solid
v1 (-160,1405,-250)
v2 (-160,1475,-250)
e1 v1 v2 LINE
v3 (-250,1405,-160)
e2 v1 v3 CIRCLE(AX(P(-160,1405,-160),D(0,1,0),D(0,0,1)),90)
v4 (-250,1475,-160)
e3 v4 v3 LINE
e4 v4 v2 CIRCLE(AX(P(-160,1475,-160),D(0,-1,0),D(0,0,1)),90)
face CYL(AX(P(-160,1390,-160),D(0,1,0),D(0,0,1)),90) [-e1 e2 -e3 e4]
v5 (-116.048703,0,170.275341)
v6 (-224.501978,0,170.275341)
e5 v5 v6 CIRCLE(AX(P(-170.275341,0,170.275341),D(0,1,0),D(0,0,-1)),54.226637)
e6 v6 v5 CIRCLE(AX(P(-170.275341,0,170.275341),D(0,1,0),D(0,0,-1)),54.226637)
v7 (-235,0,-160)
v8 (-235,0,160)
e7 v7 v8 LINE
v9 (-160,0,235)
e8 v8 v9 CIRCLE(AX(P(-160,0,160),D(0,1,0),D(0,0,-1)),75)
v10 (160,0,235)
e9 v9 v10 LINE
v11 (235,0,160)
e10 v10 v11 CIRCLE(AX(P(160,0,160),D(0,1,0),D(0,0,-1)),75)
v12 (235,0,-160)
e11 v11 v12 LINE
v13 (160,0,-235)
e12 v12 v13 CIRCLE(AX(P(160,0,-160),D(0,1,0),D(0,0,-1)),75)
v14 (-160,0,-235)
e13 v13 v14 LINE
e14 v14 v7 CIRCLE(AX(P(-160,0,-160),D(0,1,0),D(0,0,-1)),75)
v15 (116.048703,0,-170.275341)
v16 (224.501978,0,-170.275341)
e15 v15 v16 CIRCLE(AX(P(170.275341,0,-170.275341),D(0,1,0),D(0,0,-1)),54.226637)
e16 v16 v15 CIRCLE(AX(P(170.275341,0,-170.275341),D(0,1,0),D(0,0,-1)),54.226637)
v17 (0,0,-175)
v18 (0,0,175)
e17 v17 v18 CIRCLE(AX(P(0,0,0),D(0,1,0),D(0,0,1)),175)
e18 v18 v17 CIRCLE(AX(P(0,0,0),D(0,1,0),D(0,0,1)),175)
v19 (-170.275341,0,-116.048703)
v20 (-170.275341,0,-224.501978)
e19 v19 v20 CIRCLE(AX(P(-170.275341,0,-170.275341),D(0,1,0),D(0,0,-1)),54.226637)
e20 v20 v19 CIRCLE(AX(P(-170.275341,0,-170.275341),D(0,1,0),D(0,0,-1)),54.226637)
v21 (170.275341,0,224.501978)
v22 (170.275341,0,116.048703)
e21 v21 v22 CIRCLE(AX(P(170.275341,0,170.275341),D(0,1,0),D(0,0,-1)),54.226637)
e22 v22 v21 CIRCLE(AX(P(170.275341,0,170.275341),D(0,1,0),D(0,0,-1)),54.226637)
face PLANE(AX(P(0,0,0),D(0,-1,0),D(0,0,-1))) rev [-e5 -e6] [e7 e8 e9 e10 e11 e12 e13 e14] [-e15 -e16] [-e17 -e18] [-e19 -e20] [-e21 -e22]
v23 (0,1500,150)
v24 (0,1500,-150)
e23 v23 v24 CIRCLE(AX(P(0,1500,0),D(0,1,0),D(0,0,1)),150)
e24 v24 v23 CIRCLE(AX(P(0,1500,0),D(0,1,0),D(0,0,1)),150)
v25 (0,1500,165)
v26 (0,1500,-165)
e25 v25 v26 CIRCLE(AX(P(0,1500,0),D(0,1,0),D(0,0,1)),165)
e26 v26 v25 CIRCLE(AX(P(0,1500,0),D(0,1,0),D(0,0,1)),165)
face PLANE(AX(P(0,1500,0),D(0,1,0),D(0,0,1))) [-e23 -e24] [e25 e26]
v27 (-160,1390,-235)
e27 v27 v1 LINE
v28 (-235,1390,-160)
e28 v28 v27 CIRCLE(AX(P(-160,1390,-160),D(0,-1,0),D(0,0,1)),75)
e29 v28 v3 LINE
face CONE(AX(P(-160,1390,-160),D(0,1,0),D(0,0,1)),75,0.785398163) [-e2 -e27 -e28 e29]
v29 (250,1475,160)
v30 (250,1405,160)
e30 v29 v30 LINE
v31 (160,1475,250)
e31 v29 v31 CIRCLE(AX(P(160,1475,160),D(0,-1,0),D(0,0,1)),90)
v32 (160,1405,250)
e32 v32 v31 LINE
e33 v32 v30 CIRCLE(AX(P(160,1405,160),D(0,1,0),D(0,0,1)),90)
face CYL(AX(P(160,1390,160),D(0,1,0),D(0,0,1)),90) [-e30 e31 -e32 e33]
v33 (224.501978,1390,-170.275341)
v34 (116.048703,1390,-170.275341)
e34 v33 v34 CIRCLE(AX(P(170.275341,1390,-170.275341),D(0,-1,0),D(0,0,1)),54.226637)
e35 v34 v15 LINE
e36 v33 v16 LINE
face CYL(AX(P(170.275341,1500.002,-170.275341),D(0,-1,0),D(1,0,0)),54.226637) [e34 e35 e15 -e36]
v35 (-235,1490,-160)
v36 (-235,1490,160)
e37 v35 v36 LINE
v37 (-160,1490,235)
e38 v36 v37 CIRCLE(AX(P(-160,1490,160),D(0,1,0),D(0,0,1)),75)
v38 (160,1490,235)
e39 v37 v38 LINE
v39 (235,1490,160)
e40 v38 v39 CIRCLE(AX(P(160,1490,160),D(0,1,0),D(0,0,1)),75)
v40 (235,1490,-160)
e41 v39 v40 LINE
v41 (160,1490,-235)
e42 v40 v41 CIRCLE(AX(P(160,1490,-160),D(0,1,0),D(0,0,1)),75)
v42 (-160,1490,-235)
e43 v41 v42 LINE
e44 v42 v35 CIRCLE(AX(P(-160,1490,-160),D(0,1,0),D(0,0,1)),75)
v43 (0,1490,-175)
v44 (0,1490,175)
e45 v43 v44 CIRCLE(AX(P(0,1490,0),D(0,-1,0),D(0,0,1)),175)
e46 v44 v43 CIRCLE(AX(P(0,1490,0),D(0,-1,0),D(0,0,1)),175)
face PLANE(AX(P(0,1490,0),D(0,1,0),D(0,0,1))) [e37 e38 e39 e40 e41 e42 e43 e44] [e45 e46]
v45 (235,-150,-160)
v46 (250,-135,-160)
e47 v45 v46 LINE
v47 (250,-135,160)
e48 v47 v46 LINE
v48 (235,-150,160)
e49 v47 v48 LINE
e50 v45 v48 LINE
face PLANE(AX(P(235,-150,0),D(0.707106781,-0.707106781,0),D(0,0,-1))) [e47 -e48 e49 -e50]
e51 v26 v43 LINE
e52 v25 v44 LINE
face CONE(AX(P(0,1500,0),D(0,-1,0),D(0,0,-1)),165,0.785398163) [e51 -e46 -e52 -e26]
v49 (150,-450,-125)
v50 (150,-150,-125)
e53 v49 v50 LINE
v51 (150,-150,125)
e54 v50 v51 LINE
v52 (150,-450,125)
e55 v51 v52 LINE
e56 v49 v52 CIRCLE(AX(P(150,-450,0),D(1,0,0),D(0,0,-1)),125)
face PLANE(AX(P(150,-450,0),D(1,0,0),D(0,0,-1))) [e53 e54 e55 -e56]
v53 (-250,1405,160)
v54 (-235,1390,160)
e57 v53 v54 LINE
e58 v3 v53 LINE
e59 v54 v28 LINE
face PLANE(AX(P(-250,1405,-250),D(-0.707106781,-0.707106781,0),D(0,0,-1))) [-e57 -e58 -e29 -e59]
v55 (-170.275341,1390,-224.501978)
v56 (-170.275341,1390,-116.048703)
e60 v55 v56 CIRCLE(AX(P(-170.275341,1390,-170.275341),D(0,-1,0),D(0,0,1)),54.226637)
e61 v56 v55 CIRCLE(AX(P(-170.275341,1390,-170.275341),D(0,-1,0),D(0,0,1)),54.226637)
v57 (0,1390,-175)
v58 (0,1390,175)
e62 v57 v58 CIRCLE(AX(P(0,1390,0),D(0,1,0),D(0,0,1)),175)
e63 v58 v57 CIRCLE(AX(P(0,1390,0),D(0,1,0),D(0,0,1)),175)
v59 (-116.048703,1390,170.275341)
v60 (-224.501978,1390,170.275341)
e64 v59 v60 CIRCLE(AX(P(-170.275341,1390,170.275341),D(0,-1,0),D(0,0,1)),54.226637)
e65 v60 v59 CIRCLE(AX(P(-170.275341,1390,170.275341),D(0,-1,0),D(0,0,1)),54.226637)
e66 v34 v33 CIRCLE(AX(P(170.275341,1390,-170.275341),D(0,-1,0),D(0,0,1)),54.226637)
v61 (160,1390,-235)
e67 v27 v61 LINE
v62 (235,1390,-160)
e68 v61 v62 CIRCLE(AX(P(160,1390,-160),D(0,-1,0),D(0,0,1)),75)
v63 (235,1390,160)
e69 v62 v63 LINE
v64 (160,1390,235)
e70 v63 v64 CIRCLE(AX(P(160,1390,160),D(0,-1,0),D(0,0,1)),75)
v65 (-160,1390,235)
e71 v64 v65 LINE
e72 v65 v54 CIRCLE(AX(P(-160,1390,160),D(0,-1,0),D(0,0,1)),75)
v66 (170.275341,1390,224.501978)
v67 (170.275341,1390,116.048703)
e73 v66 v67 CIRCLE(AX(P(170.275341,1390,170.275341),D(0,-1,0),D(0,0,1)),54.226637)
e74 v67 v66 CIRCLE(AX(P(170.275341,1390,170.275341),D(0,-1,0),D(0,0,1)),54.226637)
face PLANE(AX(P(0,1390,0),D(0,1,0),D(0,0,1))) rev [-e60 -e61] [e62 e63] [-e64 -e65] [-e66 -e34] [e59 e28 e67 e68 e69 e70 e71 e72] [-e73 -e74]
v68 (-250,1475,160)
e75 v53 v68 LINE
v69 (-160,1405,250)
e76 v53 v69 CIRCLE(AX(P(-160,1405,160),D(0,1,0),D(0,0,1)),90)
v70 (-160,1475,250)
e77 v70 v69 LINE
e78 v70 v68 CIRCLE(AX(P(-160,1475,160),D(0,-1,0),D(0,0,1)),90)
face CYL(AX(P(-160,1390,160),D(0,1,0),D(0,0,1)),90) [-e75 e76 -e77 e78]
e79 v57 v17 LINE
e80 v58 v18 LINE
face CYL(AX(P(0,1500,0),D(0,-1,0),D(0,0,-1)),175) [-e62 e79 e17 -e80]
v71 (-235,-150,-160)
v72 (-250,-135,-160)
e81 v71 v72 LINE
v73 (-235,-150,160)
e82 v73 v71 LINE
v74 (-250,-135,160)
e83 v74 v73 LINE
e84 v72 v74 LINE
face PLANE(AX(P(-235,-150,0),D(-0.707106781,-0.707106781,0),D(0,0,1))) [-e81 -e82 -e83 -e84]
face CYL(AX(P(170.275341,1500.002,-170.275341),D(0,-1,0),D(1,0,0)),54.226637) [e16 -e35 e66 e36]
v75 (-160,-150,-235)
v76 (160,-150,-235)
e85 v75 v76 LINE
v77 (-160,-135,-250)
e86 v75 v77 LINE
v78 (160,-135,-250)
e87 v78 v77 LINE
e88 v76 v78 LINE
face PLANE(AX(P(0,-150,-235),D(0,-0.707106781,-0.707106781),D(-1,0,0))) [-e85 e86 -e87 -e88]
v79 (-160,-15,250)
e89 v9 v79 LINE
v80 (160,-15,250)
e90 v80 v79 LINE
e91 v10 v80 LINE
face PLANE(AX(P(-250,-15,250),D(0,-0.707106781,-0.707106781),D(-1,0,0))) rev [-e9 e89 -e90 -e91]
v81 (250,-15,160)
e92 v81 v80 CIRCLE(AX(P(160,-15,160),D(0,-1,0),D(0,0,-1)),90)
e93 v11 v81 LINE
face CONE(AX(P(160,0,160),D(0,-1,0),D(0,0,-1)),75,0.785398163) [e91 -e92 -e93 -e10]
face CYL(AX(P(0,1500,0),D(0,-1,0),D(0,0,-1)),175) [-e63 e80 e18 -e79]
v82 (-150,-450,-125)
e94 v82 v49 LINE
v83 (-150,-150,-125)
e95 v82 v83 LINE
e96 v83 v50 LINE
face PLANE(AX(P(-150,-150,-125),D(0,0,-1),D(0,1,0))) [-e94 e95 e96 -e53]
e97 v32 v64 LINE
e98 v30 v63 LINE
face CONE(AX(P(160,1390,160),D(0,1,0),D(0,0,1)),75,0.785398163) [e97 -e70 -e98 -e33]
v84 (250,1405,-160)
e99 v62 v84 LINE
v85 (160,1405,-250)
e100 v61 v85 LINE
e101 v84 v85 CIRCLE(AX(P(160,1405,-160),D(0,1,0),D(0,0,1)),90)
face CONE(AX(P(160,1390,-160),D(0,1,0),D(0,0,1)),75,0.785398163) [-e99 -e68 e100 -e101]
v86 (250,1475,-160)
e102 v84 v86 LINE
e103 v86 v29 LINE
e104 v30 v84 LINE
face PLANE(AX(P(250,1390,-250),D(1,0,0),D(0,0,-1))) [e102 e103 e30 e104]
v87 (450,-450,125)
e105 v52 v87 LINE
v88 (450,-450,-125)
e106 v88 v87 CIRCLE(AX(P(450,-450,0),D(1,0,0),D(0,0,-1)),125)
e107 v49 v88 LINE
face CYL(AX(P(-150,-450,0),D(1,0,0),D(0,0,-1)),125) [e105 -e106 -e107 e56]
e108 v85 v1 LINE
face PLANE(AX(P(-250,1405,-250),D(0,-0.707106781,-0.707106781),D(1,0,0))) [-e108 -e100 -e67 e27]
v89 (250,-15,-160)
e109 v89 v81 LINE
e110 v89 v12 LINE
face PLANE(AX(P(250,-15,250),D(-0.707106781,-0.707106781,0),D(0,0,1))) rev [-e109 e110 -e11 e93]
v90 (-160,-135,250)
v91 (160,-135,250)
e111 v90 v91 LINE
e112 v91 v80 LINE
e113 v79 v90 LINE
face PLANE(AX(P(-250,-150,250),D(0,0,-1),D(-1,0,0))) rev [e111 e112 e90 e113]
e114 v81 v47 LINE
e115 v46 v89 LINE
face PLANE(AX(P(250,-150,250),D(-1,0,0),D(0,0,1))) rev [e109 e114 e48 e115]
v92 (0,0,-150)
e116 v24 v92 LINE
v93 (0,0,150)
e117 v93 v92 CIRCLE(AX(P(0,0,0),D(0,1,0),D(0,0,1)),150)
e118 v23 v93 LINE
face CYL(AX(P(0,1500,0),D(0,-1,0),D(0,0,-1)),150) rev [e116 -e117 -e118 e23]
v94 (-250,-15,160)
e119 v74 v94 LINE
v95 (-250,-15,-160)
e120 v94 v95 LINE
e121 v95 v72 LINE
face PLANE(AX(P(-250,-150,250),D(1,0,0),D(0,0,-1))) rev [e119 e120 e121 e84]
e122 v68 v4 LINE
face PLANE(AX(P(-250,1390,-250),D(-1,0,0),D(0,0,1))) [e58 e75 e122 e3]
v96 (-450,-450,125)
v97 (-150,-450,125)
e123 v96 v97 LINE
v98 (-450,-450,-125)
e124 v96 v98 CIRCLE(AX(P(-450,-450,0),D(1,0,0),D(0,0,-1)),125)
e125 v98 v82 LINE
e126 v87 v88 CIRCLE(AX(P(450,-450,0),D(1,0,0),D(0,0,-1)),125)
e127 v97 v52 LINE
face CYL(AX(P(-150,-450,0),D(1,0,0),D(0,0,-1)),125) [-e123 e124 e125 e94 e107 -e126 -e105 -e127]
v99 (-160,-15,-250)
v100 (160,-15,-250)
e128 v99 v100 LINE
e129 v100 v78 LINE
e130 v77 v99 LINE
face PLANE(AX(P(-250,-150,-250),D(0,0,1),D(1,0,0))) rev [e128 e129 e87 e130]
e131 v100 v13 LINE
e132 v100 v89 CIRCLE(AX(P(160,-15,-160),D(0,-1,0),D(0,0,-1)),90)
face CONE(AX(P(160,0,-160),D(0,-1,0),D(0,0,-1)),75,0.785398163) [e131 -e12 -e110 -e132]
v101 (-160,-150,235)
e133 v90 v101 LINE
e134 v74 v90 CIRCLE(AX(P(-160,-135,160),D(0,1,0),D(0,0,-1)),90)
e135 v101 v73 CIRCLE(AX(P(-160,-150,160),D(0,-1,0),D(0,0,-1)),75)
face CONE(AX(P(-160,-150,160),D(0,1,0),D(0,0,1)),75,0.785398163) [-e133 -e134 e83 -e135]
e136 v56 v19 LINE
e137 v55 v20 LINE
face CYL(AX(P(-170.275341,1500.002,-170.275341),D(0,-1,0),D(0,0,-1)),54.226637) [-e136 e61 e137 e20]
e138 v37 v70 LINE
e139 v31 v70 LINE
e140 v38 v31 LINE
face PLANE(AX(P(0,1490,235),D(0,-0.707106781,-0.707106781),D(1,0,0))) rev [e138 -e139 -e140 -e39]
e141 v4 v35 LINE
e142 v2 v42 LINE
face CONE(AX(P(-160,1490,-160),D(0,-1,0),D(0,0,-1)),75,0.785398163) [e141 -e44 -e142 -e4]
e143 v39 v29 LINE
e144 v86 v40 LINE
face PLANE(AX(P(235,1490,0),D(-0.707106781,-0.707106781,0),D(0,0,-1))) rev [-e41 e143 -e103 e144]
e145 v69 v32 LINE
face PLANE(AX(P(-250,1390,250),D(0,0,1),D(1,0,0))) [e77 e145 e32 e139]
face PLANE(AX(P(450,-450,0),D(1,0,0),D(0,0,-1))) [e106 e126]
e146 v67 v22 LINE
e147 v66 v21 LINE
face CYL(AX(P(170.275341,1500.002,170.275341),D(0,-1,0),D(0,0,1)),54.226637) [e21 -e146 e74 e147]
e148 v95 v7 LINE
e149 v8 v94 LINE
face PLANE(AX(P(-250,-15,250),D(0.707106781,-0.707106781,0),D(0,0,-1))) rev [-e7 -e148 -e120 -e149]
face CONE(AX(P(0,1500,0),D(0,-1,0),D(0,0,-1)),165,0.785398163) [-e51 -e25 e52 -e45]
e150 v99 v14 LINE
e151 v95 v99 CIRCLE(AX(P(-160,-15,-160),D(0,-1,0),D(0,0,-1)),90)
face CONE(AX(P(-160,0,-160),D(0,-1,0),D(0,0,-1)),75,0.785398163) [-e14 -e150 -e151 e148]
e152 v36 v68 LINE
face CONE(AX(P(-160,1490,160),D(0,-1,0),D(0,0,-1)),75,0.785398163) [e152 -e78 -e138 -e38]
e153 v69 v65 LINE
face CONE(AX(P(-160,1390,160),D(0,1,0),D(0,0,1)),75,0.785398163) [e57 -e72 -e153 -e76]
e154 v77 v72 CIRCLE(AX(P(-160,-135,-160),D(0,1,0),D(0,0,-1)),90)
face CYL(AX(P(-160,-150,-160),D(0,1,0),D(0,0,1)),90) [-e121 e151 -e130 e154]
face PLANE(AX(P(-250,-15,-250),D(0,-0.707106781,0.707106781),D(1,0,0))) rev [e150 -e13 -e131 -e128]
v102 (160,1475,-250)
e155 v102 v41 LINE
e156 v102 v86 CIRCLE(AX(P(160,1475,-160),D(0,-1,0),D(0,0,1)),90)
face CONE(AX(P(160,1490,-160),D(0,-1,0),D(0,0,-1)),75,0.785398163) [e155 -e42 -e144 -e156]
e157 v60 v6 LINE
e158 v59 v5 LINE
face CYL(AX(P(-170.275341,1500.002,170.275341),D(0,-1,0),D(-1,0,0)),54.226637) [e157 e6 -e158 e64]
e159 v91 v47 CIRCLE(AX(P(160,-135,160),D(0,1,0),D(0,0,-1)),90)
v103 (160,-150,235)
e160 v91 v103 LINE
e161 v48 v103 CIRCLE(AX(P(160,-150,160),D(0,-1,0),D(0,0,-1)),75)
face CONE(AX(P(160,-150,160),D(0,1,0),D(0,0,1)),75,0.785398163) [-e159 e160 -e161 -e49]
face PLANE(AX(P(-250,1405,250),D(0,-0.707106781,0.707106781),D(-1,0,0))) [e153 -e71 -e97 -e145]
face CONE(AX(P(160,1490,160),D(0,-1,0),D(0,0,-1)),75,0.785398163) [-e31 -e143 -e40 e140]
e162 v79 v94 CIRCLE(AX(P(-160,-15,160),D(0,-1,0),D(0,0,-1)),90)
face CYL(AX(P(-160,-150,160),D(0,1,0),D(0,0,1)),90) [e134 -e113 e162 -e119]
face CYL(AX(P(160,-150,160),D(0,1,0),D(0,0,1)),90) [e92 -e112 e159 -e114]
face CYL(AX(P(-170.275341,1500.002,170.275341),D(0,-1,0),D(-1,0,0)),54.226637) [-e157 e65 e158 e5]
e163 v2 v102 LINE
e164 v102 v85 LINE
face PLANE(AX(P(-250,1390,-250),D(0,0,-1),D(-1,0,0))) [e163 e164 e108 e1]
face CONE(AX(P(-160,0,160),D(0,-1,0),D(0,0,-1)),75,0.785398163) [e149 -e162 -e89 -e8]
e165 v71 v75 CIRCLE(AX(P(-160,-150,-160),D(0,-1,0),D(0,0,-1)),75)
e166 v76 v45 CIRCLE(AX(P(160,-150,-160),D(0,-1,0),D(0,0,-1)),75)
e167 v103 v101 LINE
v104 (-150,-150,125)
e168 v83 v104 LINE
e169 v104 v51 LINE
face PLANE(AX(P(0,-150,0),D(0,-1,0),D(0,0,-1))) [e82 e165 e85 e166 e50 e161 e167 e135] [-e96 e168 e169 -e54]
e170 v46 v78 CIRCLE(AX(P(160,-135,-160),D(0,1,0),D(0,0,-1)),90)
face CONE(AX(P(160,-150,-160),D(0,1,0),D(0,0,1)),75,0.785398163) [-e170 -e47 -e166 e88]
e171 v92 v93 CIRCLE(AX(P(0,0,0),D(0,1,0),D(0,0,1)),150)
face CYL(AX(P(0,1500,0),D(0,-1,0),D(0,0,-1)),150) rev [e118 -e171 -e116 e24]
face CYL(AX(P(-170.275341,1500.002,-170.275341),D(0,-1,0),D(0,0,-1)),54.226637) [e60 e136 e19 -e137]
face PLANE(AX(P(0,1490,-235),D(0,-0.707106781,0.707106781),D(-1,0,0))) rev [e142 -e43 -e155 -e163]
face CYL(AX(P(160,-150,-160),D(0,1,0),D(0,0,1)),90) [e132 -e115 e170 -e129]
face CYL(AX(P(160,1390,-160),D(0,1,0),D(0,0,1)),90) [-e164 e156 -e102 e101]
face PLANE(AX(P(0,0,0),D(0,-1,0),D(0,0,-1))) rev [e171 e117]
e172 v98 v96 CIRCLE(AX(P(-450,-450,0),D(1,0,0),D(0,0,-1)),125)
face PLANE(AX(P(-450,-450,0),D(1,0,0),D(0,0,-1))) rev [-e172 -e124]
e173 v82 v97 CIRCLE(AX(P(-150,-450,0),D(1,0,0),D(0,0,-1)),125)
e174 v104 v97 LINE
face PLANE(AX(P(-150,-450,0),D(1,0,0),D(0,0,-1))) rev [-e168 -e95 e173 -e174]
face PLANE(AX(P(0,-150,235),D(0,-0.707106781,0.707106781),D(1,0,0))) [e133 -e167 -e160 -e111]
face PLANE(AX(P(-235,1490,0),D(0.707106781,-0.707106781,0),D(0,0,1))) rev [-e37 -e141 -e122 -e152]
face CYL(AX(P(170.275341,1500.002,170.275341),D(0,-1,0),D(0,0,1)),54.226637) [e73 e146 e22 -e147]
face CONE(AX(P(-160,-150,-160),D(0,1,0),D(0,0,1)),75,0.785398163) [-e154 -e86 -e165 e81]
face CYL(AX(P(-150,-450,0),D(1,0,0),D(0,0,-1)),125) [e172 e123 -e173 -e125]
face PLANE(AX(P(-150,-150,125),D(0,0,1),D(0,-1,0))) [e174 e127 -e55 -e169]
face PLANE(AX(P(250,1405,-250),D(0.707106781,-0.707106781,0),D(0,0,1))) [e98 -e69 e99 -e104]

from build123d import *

# Parameters (mm, degrees)
SKETCH1_R                = 175
SKETCH1_R_2              = 150
BOSS_EXTRUDE1_DEPTH      = 1500
SKETCH2_W                = 500
SKETCH2_H                = 500
BOSS_EXTRUDE2_DEPTH      = 150
BOSS_EXTRUDE3_DEPTH      = 150
BOSS_EXTRUDE3_DEPTH_BACK = 150
BOSS_EXTRUDE4_DEPTH      = 450
BOSS_EXTRUDE4_DEPTH_BACK = 450
SKETCH4_R                = 125
CHAMFER2_SIZE            = 10
SKETCH5_W                = 500
SKETCH5_H                = 500
SKETCH5_R                = 154.887495166
BOSS_EXTRUDE5_DEPTH      = 100
BOSS_EXTRUDE6_REACH      = 1587.875
SKETCH6_R                = 54.226637303
CIRPATTERN1_COUNT        = 4
FILLET1_R                = 90
CHAMFER3_SIZE            = 15


with BuildPart() as part:
    # Sketch1 → Boss-Extrude1 (new body)
    with BuildSketch(Plane(origin=(0, 0, 0), x_dir=(1, 0, 0), z_dir=(0, 1, 0))):
        with Locations(Location((0, 0, 0), (0, 0, 270))):
            Circle(SKETCH1_R)
        with Locations(Location((0, 0, 0), (0, 0, 270))):
            Circle(SKETCH1_R_2, mode=Mode.SUBTRACT)
    extrude(amount=BOSS_EXTRUDE1_DEPTH)

    # Sketch2 → Boss-Extrude2 (add)
    with BuildSketch(Plane.XZ):
        Rectangle(SKETCH2_W, SKETCH2_H)
    extrude(amount=BOSS_EXTRUDE2_DEPTH)

    # Sketch3 → Boss-Extrude3 (add, two sides: drawn at the far end of the back side and taken through both)
    with BuildSketch(Plane(origin=(0, 0, 0), x_dir=(0, 0, -1), z_dir=(1, 0, 0)).offset(-BOSS_EXTRUDE3_DEPTH_BACK)):
        with BuildLine():
            Line((125, -150), (125, -450))
            ThreePointArc((125, -450), (0, -575), (-125, -450))
            Line((-125, -450), (-125, -150))
            Line((-125, -150), (125, -150))
        make_face()
    extrude(amount=BOSS_EXTRUDE3_DEPTH + BOSS_EXTRUDE3_DEPTH_BACK)

    # Sketch4 → Boss-Extrude4 (add, two sides: drawn at the far end of the back side and taken through both)
    with BuildSketch(Plane(origin=(0, 0, 0), x_dir=(0, 0, -1), z_dir=(1, 0, 0)).offset(-BOSS_EXTRUDE4_DEPTH_BACK)):
        with Locations((0, -450)):
            Circle(SKETCH4_R)
    extrude(amount=BOSS_EXTRUDE4_DEPTH + BOSS_EXTRUDE4_DEPTH_BACK)

    # Chamfer2
    chamfer2_edges = [part.edges().sort_by_distance(p)[0] for p in [
        (0, 1500, -175),
    ]]
    chamfer(chamfer2_edges, length=CHAMFER2_SIZE)

    # Sketch5 → Boss-Extrude5 (add)
    with BuildSketch(Plane(origin=(0, 1490, 0), x_dir=(1, 0, 0), z_dir=(0, 1, 0))):
        Rectangle(SKETCH5_W, SKETCH5_H)
        Circle(SKETCH5_R, mode=Mode.SUBTRACT)
    extrude(amount=-BOSS_EXTRUDE5_DEPTH)

    # Sketch6 → Boss-Extrude6 (add, up to next)
    with BuildSketch(Plane(origin=(0, 0, 0), x_dir=(1, 0, 0), z_dir=(0, 1, 0)), mode=Mode.PRIVATE) as boss_extrude6_sk1:
        with Locations(Location((-170.275340777, 170.275340777, 0), (0, 0, 90))):
            Circle(SKETCH6_R)
    boss_extrude6_tool1 = extrude(boss_extrude6_sk1.sketch, amount=BOSS_EXTRUDE6_REACH, mode=Mode.PRIVATE) - part.part
    boss_extrude6 = boss_extrude6_tool1.solids().sort_by_distance((-170.275341, 0, -170.275341))[0]
    add(boss_extrude6)

    # CirPattern1: Boss-Extrude6 ×4 about axis
    cirpattern1_axis = Axis((0, 0, 0), (0, 1, 0))
    for i in range(1, CIRPATTERN1_COUNT):
        add(boss_extrude6.rotate(cirpattern1_axis, i * 360 / CIRPATTERN1_COUNT))

    # Fillet1
    fillet1_edges = [part.edges().sort_by_distance(p)[0] for p in [
        (250, -75, -250),
        (250, -75, 250),
        (-250, -75, 250),
        (-250, -75, -250),
        (250, 1440, -250),
        (250, 1440, 250),
        (-250, 1440, 250),
        (-250, 1440, -250),
    ]]
    fillet(fillet1_edges, radius=FILLET1_R)

    # Chamfer3
    chamfer3_edges = [part.edges().sort_by_distance(p)[0] for p in [
        (250, -150, 0),
        (0, 0, -250),
        (-250, 0, 0),
        (0, 0, 250),
        (-223.639610307, 0, -223.639610307),
        (-223.639610307, 0, 223.639610307),
        (223.639610307, 0, 223.639610307),
        (223.639610307, 0, -223.639610307),
        (0, -150, -250),
        (0, -150, 250),
        (-250, -150, 0),
        (-223.639610307, -150, -223.639610307),
        (-223.639610307, -150, 223.639610307),
        (223.639610307, -150, 223.639610307),
        (223.639610307, -150, -223.639610307),
        (0, 1490, -250),
        (0, 1390, -250),
        (250, 1490, 0),
        (-250, 1490, 0),
        (0, 1490, 250),
        (223.639610307, 1490, -223.639610307),
        (223.639610307, 1490, 223.639610307),
        (-223.639610307, 1490, 223.639610307),
        (-223.639610307, 1490, -223.639610307),
        (-250, 1390, 0),
        (250, 1390, 0),
        (0, 1390, 250),
        (223.639610307, 1390, -223.639610307),
        (223.639610307, 1390, 223.639610307),
        (-223.639610307, 1390, 223.639610307),
        (-223.639610307, 1390, -223.639610307),
        (250, 0, 0),
    ]]
    chamfer(chamfer3_edges, length=CHAMFER3_SIZE)


solid = part.part
